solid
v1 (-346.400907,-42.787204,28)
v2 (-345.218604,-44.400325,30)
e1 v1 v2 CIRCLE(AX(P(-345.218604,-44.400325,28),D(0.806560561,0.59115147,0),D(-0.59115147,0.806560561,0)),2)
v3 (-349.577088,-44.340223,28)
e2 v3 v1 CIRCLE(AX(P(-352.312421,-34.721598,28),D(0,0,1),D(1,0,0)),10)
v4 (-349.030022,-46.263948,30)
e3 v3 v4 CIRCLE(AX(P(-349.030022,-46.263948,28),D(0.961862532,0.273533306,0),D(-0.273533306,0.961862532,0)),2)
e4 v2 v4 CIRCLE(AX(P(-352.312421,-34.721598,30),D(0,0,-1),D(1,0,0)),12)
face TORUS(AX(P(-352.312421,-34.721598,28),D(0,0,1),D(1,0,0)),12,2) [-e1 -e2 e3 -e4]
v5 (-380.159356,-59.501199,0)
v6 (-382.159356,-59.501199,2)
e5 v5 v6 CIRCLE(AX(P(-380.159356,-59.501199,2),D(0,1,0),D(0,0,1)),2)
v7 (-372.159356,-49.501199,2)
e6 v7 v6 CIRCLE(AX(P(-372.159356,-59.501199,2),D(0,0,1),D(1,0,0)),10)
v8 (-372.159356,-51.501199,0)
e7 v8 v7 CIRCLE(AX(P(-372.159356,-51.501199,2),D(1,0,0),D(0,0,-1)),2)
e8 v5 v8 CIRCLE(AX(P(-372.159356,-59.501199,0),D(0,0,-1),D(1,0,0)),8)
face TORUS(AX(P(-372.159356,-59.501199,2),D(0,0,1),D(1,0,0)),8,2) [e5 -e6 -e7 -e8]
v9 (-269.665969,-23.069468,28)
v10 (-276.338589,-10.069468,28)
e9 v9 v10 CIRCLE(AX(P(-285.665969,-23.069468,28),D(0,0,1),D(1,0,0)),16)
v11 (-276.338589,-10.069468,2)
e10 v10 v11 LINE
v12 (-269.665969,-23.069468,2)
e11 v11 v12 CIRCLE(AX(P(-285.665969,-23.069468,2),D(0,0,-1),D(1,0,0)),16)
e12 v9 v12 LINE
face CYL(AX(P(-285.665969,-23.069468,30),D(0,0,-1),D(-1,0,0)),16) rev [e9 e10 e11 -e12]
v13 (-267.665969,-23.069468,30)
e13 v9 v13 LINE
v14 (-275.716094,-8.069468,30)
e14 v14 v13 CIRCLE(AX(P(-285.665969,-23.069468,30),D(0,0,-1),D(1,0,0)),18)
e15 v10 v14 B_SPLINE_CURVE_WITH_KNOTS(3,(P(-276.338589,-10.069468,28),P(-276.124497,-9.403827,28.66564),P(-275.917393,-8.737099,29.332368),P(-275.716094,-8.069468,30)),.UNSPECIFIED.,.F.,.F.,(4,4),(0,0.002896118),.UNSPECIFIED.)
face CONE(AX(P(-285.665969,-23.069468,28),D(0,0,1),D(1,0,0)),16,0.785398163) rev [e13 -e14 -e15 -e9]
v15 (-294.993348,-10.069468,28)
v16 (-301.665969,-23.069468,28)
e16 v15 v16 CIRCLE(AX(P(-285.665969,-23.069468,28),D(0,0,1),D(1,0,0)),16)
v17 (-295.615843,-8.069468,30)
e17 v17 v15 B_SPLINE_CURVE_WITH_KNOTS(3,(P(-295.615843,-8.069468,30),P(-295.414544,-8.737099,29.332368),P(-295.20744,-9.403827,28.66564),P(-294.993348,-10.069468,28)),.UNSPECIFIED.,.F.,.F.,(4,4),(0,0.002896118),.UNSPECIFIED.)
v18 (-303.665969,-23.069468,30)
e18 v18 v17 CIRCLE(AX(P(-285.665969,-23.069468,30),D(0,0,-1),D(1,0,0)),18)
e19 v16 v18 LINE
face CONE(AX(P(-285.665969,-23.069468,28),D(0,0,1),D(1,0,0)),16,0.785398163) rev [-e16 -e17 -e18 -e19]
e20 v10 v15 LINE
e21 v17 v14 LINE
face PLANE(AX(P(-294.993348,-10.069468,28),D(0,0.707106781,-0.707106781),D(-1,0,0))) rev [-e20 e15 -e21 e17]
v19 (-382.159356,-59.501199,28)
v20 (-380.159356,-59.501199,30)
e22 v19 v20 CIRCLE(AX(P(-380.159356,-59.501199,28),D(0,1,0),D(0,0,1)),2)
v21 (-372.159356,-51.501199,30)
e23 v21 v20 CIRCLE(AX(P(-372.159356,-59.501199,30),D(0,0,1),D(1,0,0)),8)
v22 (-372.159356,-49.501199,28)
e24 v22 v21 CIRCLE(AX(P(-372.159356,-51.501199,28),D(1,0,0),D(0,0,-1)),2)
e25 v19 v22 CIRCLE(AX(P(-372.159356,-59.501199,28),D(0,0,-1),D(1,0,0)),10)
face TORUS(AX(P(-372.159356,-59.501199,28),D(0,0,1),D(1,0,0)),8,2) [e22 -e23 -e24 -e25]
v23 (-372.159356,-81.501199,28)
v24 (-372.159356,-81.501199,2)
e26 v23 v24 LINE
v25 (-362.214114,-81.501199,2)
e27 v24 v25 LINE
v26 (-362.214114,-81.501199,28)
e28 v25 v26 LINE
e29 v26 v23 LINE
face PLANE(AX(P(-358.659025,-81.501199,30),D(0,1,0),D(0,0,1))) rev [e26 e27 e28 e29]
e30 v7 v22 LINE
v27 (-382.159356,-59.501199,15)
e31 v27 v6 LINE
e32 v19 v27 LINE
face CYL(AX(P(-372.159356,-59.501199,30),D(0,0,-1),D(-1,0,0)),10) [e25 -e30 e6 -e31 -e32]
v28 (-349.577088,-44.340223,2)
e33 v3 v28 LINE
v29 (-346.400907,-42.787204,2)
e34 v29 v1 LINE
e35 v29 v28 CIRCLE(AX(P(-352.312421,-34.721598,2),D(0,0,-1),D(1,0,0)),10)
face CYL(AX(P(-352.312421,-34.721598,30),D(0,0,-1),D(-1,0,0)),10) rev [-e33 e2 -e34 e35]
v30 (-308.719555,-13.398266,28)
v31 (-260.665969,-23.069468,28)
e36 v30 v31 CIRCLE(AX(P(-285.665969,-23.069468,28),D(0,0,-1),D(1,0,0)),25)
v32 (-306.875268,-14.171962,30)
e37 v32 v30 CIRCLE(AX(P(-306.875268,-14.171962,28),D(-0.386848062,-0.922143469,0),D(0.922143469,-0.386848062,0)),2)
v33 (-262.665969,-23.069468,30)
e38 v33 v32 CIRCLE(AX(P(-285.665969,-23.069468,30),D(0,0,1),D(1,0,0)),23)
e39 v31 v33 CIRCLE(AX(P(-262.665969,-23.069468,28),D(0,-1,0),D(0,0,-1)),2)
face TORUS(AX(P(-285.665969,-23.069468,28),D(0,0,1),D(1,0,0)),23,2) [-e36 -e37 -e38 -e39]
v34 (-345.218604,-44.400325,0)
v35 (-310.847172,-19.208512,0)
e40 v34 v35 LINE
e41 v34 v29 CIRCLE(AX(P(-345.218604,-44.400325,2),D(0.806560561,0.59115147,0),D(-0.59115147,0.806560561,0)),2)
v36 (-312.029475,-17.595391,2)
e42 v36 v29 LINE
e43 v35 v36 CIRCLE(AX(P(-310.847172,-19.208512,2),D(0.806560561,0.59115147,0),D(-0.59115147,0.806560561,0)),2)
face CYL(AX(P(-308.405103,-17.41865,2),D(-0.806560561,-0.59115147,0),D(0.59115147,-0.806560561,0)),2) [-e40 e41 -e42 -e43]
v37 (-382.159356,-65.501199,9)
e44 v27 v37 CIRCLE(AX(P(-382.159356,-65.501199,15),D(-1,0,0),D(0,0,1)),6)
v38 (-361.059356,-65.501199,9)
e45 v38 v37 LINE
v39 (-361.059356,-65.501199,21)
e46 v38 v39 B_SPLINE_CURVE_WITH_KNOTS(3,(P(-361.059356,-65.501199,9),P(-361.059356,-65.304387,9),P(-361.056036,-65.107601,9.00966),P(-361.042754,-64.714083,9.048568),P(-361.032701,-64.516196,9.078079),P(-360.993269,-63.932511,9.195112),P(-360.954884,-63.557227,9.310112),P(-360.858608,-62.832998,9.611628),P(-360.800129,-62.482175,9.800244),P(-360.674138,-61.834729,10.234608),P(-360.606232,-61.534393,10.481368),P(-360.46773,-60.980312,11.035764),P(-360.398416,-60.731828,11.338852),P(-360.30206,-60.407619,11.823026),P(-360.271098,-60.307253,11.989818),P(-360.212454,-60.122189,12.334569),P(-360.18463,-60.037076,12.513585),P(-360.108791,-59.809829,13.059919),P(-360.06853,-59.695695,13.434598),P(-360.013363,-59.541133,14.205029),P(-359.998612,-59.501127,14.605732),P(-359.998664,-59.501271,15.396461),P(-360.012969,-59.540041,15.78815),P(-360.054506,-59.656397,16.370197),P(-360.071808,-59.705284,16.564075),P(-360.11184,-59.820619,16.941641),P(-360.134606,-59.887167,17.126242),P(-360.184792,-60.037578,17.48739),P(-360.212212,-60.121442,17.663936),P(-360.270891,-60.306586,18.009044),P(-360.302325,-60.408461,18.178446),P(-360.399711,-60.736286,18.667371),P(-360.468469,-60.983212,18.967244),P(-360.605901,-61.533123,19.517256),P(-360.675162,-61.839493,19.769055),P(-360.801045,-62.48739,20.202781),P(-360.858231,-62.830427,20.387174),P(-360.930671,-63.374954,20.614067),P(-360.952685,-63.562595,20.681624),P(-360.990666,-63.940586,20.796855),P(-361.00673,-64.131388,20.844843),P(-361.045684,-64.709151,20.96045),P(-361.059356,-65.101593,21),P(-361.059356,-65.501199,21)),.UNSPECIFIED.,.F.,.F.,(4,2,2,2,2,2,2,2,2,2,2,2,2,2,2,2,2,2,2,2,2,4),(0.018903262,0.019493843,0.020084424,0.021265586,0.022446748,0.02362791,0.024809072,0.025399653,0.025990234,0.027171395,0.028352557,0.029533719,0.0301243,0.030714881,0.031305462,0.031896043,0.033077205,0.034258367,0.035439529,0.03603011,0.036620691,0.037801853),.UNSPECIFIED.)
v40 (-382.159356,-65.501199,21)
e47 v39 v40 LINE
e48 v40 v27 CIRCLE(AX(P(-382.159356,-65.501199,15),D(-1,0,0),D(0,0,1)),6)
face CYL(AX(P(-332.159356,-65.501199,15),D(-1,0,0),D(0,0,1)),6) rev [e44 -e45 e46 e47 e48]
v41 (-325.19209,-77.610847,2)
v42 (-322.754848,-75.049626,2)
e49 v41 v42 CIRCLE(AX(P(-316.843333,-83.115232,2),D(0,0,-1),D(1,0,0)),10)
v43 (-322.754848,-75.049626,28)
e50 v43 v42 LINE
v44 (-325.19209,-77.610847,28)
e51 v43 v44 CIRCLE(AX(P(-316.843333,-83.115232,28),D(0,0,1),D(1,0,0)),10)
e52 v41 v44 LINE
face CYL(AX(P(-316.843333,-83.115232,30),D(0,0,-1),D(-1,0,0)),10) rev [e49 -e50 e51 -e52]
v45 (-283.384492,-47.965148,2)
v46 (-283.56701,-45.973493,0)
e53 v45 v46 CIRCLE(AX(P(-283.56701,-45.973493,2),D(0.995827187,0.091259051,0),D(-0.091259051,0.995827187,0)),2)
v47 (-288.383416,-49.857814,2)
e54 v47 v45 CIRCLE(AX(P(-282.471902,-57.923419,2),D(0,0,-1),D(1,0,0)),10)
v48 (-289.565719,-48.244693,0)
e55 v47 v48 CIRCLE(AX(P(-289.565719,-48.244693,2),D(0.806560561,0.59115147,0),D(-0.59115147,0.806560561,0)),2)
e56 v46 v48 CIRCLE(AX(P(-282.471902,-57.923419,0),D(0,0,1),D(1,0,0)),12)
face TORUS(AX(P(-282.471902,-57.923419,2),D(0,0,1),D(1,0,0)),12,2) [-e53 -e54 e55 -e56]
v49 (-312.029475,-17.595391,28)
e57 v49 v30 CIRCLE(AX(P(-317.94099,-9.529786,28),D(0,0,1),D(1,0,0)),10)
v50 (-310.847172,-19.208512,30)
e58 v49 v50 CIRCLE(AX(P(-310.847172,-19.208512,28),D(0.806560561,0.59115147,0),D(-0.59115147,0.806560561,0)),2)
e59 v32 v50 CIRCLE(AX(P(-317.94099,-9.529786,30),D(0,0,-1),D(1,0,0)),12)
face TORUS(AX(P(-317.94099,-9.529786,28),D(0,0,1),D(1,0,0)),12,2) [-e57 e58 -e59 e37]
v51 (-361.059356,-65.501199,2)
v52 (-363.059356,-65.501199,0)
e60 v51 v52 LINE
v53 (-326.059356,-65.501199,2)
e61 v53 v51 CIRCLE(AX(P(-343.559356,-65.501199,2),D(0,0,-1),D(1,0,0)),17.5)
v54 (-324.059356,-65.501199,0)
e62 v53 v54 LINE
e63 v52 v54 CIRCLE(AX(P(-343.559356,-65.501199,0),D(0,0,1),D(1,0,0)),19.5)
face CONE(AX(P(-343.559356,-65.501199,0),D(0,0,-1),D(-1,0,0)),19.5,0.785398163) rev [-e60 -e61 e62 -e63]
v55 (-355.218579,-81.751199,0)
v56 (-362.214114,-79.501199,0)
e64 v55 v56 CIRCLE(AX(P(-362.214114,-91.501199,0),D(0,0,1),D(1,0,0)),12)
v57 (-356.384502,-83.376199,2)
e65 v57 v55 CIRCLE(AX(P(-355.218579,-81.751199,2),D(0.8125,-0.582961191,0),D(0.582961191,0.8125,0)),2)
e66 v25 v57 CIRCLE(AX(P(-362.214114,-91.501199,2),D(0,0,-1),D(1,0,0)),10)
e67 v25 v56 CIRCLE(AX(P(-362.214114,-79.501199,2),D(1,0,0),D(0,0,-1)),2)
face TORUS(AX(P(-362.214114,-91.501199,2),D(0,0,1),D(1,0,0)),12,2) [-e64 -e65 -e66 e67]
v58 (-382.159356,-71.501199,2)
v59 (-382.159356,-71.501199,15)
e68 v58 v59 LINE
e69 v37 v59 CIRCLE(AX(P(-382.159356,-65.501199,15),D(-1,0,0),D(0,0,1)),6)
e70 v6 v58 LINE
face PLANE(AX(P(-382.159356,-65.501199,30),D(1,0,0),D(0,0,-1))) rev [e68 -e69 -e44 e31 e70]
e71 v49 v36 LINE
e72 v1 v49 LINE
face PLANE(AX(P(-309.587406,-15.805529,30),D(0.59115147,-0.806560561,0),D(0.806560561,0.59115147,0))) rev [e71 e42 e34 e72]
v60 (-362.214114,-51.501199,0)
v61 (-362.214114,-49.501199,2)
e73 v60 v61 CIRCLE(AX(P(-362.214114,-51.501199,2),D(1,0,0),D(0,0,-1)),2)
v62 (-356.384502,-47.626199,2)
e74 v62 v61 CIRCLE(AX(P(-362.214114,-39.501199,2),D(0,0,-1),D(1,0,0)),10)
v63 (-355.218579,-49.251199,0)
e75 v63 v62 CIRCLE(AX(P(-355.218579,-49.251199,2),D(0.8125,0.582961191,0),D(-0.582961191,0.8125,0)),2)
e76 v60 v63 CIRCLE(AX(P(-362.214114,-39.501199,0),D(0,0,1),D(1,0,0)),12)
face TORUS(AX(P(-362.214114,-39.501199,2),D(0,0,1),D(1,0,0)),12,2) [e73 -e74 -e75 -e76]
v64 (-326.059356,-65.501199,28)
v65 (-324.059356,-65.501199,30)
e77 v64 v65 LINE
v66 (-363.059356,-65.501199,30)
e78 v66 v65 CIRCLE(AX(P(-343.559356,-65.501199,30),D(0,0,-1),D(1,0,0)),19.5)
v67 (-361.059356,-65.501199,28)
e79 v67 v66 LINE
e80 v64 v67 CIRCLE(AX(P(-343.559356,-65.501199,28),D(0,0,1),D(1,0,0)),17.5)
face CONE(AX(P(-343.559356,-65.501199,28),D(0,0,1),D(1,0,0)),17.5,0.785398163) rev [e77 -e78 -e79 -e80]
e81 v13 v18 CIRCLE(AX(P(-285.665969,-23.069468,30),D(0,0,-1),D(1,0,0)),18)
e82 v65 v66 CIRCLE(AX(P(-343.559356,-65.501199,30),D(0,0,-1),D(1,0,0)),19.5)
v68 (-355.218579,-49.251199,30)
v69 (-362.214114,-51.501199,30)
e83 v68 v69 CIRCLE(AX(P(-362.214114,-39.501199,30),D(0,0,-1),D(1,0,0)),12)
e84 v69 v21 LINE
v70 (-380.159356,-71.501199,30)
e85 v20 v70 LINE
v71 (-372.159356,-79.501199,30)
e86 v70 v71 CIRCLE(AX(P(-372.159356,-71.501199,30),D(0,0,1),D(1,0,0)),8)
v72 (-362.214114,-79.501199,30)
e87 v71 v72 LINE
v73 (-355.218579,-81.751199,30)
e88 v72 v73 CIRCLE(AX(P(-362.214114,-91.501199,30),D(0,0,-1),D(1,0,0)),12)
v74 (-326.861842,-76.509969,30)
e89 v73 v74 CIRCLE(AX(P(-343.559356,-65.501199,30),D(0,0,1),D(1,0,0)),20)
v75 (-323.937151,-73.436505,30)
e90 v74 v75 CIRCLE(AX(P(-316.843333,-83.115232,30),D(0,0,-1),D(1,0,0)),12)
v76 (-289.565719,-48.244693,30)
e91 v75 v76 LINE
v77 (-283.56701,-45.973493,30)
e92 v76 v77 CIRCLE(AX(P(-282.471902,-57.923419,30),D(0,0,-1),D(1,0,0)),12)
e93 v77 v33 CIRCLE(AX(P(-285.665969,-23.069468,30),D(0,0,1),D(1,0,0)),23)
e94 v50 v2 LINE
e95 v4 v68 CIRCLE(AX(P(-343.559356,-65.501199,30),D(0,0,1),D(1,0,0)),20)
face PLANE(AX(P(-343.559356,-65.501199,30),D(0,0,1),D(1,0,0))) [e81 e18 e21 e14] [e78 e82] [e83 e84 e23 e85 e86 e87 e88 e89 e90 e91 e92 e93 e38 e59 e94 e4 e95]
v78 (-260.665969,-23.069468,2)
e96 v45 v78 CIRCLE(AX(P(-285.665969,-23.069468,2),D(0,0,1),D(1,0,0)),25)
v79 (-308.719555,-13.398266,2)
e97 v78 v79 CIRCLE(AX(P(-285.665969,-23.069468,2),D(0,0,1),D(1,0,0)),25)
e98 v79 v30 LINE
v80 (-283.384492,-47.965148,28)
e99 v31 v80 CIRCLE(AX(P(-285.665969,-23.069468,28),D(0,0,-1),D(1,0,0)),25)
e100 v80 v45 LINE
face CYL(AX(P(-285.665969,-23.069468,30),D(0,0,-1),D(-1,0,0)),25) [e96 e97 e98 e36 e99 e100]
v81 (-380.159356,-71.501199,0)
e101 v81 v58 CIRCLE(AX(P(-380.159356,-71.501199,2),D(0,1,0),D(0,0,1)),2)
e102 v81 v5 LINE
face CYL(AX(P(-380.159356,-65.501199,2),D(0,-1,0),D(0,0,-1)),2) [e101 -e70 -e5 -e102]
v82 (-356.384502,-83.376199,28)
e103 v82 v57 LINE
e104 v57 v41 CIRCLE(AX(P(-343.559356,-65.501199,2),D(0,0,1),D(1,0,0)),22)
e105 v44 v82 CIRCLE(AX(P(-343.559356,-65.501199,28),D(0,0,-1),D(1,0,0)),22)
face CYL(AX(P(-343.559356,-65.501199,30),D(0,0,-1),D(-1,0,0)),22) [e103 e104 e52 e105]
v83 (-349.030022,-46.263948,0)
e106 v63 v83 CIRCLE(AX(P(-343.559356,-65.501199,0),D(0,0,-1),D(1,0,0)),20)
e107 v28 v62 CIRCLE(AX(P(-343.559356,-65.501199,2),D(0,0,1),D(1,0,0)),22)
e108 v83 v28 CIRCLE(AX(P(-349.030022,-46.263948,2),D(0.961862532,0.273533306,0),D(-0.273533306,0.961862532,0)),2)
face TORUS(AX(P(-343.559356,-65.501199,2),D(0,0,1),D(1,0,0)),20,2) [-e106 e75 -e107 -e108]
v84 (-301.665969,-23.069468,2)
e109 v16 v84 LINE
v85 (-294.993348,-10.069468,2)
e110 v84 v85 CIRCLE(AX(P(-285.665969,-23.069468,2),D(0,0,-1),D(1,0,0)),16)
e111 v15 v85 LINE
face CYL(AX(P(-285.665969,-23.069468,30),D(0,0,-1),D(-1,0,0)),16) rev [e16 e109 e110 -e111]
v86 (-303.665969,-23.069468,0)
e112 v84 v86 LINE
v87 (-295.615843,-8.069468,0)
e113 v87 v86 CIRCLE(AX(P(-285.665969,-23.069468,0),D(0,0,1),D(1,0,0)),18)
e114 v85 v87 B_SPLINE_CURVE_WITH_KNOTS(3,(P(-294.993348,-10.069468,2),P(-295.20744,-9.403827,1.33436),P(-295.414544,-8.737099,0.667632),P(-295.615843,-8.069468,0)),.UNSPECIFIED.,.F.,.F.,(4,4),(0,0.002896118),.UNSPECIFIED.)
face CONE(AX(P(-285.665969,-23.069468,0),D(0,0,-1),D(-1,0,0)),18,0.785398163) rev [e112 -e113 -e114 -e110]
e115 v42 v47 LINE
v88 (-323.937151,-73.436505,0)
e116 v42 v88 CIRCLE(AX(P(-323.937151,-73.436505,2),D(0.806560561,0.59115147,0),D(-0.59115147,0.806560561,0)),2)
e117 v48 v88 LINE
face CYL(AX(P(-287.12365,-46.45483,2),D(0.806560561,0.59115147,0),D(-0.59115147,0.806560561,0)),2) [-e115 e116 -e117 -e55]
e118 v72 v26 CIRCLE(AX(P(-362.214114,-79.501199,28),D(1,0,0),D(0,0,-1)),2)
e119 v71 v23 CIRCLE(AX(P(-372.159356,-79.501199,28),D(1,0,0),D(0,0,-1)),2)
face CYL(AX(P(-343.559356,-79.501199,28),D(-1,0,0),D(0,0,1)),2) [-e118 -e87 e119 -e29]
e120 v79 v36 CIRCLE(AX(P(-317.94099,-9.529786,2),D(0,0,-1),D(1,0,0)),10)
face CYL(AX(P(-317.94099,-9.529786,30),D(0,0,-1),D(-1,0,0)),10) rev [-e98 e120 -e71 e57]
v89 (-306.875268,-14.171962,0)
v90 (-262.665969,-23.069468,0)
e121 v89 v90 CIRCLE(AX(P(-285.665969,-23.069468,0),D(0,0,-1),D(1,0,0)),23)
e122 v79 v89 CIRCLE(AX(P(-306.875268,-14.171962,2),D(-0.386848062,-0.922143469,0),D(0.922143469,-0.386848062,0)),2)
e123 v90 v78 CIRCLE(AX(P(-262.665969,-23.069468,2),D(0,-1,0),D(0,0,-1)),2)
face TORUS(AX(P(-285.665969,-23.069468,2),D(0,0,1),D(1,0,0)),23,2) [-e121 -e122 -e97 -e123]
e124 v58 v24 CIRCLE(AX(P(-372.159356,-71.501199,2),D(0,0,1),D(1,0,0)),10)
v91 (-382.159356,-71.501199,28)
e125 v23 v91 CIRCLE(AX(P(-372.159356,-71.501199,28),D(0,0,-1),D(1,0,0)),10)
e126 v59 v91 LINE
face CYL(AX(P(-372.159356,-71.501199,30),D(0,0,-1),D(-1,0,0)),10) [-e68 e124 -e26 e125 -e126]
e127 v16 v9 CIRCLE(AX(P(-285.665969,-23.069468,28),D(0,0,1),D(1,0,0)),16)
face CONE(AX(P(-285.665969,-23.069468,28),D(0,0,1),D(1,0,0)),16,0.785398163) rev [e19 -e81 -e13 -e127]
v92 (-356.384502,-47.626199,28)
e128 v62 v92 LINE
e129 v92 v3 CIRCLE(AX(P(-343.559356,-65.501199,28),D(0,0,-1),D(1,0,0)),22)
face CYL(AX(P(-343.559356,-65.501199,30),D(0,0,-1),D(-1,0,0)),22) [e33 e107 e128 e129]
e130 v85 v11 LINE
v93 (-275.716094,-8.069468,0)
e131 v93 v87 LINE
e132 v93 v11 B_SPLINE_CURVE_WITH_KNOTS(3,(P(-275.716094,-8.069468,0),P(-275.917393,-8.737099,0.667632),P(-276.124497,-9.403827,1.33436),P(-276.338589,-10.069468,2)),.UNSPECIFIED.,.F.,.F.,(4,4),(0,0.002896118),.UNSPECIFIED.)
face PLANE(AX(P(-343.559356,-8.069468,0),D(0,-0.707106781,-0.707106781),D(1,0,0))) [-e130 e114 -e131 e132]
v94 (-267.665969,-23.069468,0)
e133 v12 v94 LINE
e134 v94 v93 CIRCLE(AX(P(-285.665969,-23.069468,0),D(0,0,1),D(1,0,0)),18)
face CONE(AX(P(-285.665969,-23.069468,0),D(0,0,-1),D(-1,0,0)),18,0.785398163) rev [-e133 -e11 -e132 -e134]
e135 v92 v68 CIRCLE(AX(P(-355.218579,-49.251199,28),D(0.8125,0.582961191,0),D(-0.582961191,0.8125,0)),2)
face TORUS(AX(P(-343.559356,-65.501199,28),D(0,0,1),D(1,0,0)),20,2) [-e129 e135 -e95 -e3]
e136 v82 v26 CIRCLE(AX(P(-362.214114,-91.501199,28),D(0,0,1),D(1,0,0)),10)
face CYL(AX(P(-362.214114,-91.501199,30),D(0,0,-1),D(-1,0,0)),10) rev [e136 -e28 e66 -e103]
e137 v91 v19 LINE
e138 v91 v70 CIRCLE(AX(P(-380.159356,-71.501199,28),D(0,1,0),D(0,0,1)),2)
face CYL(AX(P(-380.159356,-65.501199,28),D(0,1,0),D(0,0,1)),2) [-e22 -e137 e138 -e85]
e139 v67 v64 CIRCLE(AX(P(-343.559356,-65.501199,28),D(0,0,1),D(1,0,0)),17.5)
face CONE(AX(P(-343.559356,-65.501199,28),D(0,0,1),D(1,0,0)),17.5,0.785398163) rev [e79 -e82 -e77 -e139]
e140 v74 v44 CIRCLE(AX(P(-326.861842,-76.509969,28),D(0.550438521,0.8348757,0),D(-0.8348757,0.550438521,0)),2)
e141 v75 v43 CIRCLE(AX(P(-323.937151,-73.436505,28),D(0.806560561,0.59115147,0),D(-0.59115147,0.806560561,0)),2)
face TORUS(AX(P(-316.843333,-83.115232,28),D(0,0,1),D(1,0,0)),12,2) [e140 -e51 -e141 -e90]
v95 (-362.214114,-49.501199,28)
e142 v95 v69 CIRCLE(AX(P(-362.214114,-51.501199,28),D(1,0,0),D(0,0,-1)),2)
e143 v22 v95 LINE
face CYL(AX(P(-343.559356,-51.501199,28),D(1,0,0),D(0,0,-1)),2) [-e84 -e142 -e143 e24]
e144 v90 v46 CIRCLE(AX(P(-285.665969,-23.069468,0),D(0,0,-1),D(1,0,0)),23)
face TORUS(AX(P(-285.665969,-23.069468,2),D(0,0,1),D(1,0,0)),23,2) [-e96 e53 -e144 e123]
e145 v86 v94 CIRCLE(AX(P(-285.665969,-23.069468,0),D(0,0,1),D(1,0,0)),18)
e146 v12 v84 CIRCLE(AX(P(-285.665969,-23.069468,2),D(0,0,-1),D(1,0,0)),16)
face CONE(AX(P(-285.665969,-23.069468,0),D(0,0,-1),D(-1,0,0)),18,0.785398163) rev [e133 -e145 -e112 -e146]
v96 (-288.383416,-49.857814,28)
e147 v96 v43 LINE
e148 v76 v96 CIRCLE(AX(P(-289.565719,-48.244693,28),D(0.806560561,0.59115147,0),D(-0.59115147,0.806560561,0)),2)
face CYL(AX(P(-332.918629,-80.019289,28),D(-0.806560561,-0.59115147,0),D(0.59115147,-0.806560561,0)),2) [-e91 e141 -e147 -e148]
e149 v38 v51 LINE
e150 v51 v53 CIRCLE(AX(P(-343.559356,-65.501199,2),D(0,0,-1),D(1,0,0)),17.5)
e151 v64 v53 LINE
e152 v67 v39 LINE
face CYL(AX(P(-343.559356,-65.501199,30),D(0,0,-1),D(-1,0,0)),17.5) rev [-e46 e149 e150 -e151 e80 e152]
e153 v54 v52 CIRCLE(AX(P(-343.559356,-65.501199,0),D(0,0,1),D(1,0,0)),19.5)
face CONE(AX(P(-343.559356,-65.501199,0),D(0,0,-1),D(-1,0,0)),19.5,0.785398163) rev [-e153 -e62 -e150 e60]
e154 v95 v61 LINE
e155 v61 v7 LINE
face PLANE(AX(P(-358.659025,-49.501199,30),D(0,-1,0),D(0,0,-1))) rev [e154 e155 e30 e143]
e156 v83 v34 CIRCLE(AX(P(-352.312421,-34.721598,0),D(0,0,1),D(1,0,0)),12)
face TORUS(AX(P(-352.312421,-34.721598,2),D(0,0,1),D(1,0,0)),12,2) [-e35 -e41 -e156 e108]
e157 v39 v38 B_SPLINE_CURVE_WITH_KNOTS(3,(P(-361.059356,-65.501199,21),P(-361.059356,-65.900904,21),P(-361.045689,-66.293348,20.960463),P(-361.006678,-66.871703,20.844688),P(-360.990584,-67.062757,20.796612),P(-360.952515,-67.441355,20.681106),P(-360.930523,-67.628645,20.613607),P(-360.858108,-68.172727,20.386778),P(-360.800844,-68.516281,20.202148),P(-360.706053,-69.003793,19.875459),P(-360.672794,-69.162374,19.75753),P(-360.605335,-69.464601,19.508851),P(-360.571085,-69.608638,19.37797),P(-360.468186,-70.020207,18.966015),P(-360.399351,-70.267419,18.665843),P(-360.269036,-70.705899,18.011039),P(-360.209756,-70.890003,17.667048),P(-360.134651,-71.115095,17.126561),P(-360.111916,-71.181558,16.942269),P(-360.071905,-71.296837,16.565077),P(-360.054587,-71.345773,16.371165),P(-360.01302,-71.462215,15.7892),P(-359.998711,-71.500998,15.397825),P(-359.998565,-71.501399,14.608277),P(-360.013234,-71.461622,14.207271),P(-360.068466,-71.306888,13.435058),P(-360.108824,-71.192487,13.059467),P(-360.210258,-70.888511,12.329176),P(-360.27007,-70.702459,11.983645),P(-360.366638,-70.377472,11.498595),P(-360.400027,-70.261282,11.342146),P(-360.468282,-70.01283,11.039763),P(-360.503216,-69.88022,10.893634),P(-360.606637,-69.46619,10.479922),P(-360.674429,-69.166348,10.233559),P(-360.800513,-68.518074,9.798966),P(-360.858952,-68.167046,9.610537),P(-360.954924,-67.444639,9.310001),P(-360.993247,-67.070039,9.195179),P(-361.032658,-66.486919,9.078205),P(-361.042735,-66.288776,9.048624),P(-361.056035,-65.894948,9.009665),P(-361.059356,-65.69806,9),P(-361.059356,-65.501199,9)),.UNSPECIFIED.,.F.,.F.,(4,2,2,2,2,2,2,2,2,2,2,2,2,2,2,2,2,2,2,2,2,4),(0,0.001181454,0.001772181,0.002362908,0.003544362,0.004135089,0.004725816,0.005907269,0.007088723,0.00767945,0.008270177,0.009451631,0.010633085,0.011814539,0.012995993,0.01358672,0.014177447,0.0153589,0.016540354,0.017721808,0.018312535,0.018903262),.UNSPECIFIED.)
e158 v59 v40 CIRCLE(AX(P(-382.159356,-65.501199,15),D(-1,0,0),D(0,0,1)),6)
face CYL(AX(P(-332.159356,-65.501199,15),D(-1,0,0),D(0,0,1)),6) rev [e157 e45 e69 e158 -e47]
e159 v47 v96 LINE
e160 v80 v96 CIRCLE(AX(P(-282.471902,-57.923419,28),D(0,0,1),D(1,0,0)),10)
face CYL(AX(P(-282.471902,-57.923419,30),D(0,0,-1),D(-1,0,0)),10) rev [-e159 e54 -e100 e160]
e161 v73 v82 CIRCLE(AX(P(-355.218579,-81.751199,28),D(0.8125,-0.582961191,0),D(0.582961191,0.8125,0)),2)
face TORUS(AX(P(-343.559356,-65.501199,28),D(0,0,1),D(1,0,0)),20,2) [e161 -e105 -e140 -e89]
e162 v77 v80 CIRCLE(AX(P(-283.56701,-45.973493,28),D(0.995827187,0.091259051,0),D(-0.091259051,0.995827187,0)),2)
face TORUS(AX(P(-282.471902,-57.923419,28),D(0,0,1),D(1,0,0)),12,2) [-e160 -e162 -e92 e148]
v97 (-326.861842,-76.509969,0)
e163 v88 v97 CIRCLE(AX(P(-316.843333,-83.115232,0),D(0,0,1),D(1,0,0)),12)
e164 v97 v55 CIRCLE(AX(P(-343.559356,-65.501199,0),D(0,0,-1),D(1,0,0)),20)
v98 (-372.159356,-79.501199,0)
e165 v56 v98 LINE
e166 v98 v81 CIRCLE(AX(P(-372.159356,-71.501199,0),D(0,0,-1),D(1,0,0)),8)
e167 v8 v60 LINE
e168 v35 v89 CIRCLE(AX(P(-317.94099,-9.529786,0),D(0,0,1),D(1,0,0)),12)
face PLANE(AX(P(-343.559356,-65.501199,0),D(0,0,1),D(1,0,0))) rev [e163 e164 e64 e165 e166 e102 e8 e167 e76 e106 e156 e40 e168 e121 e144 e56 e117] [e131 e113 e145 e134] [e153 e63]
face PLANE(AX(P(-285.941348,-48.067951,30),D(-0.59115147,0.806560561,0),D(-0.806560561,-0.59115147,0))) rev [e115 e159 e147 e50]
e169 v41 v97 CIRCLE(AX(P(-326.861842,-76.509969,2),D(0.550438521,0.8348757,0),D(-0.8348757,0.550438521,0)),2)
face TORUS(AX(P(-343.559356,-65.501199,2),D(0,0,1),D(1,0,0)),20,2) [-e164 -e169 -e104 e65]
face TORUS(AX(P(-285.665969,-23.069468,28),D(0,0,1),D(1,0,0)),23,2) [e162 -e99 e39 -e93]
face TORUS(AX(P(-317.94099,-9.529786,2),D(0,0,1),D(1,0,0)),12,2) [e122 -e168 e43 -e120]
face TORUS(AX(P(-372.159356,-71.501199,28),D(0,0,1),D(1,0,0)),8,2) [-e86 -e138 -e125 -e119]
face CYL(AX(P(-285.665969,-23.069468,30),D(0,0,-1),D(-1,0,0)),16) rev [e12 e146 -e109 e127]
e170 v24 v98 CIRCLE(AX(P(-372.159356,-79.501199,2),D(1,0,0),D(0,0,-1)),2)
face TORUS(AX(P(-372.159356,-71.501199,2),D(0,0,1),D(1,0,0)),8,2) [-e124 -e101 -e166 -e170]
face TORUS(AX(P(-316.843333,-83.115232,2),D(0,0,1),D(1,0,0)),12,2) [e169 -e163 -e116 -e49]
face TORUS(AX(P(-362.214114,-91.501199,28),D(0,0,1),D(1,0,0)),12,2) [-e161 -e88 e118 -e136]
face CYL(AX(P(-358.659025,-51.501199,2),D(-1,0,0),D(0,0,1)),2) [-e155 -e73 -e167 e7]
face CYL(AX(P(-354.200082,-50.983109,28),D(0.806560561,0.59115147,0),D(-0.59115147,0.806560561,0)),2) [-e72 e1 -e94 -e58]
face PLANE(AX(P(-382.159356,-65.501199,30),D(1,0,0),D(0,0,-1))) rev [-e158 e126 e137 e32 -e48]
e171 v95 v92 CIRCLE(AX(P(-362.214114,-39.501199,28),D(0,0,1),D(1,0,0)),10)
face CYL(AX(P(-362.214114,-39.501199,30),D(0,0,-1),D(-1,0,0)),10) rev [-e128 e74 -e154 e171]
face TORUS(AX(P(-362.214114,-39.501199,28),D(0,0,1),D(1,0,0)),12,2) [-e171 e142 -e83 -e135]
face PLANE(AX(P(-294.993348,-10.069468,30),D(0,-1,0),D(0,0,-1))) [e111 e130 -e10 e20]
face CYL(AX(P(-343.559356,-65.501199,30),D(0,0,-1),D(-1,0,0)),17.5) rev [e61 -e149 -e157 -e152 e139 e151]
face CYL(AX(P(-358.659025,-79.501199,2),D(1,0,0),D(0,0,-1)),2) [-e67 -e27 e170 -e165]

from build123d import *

# Parameters (mm, degrees)
SKETCH_1_R          = 17.5
EXTRUDE_1_DEPTH     = 30
FILLET_1_R          = 10
FILLET_2_R          = 2
CHAMFER_1_SIZE      = 2
SKETCH_2_R          = 6
CUT_EXTRUDE_1_DEPTH = 50


with BuildPart() as part:
    # 草图1 → 凸台-拉伸1 (new body)
    with BuildSketch(Plane.XY):
        with BuildLine():
            Line((-309.587406351, -15.805528725), (-347.990135407, -43.951995119))
            ThreePointArc((-347.990135407, -43.951995119), (-353.711105355, -45.983464105), (-358.659024526, -49.501199067))
            Line((-358.659024526, -49.501199067), (-382.159355655, -49.501199067))
            Line((-382.159355655, -49.501199067), (-382.159355655, -65.501199067))
            Line((-382.159355655, -65.501199067), (-382.159355655, -81.501199067))
            Line((-382.159355655, -81.501199067), (-358.659024526, -81.501199067))
            ThreePointArc((-358.659024526, -81.501199067), (-340.209418876, -87.244656096), (-324.344076601, -76.214417578))
            Line((-324.344076601, -76.214417578), (-285.941347545, -48.067951184))
            ThreePointArc((-285.941347545, -48.067951184), (-265.501954489, -8.290681148), (-309.587406351, -15.805528725))
        make_face()
        with Locations((-343.559355655, -65.501199067)):
            Circle(SKETCH_1_R, mode=Mode.SUBTRACT)
        with BuildLine():
            Line((-294.993347579, -10.069467902), (-276.338589473, -10.069467902))
            ThreePointArc((-276.338589473, -10.069467902), (-285.665968526, -39.069467902), (-294.993347579, -10.069467902))
        make_face(mode=Mode.SUBTRACT)
    extrude(amount=EXTRUDE_1_DEPTH)

    # 圆角1
    fillet_1_edges = [part.edges().sort_by_distance(p)[0] for p in [
        (-347.990135407, -43.951995119, 15),
        (-309.587406351, -15.805528725, 15),
        (-285.941347545, -48.067951184, 15),
        (-324.344076601, -76.214417578, 15),
        (-358.659024526, -81.501199067, 15),
        (-382.159355655, -81.501199067, 15),
        (-382.159355655, -49.501199067, 15),
        (-358.659024526, -49.501199067, 15),
    ]]
    fillet(fillet_1_edges, radius=FILLET_1_R)

    # 圆角2
    fillet_2_edges = [part.edges().sort_by_distance(p)[0] for p in [
        (-353.122981052, -45.688650789, 0),
        (-353.122981052, -45.688650789, 30),
        (-329.215190996, -30.191297509, 0),
        (-329.215190996, -30.191297509, 30),
        (-265.501954489, -8.290681148, 0),
        (-265.501954489, -8.290681148, 30),
        (-305.56913219, -62.453719969, 0),
        (-305.56913219, -62.453719969, 30),
        (-339.560781684, -87.134770344, 0),
        (-339.560781684, -87.134770344, 30),
        (-367.186734708, -81.501199067, 0),
        (-367.186734708, -81.501199067, 30),
        (-382.159355655, -65.501199067, 0),
        (-367.186734708, -49.501199067, 0),
        (-379.230423467, -52.430131255, 0),
        (-379.230423467, -78.572266879, 0),
        (-382.159355655, -65.501199067, 30),
        (-367.186734708, -49.501199067, 30),
        (-379.230423467, -52.430131255, 30),
        (-379.230423467, -78.572266879, 30),
        (-347.919818401, -43.705196344, 0),
        (-347.919818401, -43.705196344, 30),
        (-310.08888806, -15.722079028, 0),
        (-310.08888806, -15.722079028, 30),
        (-324.087558519, -76.221669503, 0),
        (-324.087558519, -76.221669503, 30),
        (-359.152251583, -81.981482685, 0),
        (-359.152251583, -81.981482685, 30),
        (-359.152251583, -49.020915449, 0),
        (-359.152251583, -49.020915449, 30),
        (-286.012756057, -48.571288626, 0),
        (-286.012756057, -48.571288626, 30),
    ]]
    fillet(fillet_2_edges, radius=FILLET_2_R)

    # 倒角1
    chamfer_1_edges = [part.edges().sort_by_distance(p)[0] for p in [
        (-285.665968526, -39.069467902, 0),
        (-285.665968526, -10.069467902, 0),
        (-285.665968526, -39.069467902, 30),
        (-285.665968526, -10.069467902, 30),
        (-361.059355655, -65.501199067, 0),
        (-361.059355655, -65.501199067, 30),
    ]]
    chamfer(chamfer_1_edges, length=CHAMFER_1_SIZE)

    # 草图2 → 切除-拉伸1 (cut)
    with BuildSketch(Plane.ZY.offset(382.159355655)):
        with Locations((15, -65.501199067)):
            Circle(SKETCH_2_R)
    extrude(amount=-CUT_EXTRUDE_1_DEPTH, mode=Mode.SUBTRACT)


solid = part.part
